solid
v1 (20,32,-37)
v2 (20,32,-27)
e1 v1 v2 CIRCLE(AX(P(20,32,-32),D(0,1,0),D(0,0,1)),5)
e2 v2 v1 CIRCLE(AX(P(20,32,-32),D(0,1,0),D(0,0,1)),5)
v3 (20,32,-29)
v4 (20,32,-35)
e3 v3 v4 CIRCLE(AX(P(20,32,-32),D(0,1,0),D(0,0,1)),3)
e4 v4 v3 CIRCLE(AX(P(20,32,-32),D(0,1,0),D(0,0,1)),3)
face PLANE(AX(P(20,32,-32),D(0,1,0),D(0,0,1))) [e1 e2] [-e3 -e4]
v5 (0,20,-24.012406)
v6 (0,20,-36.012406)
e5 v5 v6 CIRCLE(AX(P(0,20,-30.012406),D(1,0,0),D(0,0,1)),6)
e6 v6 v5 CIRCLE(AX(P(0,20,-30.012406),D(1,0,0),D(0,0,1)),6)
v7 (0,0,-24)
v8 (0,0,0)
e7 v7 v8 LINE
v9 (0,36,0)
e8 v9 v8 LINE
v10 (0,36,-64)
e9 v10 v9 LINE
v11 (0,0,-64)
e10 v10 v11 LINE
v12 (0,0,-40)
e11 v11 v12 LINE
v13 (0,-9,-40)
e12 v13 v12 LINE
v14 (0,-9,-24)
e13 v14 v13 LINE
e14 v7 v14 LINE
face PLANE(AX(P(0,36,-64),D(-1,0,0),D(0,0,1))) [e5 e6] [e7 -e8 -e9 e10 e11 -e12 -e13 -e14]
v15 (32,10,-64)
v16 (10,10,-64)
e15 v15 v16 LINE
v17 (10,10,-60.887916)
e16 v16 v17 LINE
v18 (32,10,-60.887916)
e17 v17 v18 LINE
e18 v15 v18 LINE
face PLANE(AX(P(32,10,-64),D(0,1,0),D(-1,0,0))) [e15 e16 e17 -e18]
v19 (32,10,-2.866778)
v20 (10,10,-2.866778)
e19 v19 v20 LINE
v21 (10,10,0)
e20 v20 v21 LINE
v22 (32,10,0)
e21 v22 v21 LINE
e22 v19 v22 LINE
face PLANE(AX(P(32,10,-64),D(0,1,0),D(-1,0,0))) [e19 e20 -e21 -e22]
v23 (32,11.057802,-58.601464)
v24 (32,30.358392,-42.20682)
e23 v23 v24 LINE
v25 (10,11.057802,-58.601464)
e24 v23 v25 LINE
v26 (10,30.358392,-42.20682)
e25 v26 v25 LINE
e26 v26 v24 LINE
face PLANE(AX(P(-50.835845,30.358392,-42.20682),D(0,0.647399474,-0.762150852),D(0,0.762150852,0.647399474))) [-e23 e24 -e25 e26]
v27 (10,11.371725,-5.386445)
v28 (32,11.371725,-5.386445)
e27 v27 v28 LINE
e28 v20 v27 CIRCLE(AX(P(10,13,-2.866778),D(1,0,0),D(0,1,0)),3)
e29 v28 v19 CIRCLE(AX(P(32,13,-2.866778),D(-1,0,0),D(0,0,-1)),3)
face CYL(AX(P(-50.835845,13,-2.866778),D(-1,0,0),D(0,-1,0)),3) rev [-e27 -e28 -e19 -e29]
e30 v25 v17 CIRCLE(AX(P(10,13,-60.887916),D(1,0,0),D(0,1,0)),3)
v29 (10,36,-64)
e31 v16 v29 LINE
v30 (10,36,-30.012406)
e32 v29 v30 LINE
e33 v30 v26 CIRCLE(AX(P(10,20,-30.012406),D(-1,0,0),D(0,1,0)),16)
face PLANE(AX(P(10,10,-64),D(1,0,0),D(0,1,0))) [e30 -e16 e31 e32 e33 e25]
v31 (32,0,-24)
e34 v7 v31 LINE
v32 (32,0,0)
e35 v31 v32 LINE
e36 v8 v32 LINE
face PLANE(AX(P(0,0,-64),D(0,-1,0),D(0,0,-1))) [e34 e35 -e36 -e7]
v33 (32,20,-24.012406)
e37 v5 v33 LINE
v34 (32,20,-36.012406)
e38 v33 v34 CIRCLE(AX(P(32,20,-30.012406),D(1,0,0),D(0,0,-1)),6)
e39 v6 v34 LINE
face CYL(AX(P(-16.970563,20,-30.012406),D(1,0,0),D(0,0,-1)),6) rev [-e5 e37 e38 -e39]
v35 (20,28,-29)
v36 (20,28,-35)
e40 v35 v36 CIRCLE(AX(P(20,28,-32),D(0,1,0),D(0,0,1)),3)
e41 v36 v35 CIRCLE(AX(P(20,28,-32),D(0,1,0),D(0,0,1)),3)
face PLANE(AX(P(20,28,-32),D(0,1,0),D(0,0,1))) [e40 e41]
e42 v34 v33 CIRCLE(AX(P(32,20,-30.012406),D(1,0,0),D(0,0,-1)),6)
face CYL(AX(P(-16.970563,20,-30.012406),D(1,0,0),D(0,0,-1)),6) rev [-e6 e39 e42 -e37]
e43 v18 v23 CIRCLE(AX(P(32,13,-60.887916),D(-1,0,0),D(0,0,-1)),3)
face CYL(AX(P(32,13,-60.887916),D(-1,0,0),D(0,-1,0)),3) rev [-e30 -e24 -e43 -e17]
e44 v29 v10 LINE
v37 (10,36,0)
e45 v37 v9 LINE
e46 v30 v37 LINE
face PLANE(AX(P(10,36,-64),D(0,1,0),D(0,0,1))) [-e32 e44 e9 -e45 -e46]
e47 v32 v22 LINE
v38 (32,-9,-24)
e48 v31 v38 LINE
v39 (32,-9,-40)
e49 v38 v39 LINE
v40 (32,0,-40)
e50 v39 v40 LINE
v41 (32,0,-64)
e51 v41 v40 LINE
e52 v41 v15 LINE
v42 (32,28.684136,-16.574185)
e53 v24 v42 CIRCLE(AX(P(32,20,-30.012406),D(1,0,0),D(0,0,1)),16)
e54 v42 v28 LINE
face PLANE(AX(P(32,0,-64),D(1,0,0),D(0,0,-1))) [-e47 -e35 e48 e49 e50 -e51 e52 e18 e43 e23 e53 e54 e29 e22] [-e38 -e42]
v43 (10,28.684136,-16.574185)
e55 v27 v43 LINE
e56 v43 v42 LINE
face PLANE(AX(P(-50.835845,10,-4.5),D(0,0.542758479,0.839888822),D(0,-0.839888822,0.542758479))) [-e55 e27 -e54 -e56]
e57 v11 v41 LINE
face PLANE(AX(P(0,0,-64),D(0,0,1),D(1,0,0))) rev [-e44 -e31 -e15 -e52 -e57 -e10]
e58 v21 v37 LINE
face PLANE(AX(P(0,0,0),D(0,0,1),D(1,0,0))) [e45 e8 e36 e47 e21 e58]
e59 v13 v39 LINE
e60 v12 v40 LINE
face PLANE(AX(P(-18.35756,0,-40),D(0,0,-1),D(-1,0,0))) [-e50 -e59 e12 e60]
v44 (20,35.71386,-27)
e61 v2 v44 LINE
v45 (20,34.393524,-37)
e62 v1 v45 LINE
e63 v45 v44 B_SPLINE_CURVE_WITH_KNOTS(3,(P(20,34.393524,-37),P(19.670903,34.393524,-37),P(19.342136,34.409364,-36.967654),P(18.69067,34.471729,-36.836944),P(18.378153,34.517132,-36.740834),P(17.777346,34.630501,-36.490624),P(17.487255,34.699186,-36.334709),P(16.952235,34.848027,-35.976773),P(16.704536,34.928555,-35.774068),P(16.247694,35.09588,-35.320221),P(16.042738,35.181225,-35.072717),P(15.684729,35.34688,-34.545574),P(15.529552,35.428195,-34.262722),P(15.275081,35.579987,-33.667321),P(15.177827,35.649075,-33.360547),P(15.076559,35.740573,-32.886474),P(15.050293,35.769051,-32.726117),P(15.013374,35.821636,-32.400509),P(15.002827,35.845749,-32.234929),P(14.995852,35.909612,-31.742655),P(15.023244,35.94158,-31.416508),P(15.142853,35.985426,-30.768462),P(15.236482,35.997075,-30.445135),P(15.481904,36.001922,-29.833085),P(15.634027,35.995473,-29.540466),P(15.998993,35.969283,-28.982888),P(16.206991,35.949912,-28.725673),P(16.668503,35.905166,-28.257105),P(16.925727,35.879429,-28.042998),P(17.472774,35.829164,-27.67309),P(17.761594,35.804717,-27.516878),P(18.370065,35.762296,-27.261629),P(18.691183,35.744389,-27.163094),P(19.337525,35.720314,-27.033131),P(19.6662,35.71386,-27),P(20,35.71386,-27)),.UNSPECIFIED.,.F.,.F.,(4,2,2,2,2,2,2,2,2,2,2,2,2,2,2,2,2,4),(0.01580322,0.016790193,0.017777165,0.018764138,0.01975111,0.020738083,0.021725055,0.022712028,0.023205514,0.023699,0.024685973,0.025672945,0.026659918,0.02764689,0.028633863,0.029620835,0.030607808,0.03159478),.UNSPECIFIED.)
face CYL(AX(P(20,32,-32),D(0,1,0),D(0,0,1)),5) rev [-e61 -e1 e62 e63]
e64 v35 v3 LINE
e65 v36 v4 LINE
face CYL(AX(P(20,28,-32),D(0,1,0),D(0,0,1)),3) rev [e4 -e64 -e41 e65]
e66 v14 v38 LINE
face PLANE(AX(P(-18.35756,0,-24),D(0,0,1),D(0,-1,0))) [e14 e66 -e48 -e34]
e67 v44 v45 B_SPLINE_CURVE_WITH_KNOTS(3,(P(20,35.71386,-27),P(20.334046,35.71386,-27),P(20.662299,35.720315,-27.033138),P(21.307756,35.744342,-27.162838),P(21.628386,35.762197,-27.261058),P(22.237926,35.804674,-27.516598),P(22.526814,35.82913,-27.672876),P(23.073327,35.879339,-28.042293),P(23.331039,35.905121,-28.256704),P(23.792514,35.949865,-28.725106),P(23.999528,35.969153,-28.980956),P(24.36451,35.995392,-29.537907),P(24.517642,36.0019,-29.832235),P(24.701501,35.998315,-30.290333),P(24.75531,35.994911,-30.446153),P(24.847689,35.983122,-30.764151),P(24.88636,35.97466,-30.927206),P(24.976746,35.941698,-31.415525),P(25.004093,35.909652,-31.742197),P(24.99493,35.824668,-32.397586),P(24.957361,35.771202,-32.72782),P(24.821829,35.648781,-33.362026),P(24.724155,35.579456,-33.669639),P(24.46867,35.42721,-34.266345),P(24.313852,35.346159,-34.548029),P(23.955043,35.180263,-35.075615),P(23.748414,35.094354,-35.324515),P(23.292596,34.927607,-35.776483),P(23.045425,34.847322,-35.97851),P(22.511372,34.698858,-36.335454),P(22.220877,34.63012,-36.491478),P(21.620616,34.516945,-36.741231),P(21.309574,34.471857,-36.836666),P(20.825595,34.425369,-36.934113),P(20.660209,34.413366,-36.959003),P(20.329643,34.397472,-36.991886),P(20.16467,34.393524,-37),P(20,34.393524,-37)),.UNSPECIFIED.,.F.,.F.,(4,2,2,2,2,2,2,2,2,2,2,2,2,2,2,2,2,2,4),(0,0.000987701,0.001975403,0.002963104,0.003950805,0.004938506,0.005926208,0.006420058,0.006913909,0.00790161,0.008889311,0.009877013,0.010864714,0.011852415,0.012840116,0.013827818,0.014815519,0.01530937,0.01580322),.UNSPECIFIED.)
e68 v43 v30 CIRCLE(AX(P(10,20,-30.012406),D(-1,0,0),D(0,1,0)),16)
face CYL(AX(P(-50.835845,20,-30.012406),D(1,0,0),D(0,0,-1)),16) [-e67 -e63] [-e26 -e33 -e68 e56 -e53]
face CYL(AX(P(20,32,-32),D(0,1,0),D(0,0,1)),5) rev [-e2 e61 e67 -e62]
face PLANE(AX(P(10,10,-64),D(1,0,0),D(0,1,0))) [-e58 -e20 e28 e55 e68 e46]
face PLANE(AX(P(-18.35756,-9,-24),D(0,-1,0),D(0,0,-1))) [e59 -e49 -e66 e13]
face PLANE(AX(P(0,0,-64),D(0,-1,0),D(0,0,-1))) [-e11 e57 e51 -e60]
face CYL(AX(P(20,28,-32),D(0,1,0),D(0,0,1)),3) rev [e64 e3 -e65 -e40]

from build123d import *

# Parameters (mm, degrees)
JAW_BODY_DEPTH         = 64
PIVOT_BOSS_DEPTH       = 22
PIVOT_BORE_SKETCH_R    = 6
PIVOT_BORE_12_DEPTH    = 32
GUIDE_KEY_SKETCH_W     = 16
GUIDE_KEY_SKETCH_H     = 9
GUIDE_KEY_DEPTH        = 32
PIVOT_BOSS_FILLET_R3_R = 3
COUNTERBORE_SKETCH_R   = 5
COUNTERBORE_10X4_DEPTH = 4
SCREW_HOLE_SKETCH_R    = 3
SCREW_HOLE_6X4_DEPTH   = 4


with BuildPart() as part:
    # Jaw Body Profile Sketch → Jaw Body (new body)
    with BuildSketch(Plane.XY):
        Polygon((0, 0), (32, 0), (32, 10), (10, 10), (10, 36), (0, 36), align=None)
    extrude(amount=-JAW_BODY_DEPTH)

    # Pivot Boss Sketch → Pivot Boss (add)
    with BuildSketch(Plane(origin=(32, 0, 0), x_dir=(0, 0, -1), z_dir=(1, 0, 0))):
        with BuildLine():
            Line((4.5, 10), (16.574185034, 28.68413566))
            ThreePointArc((16.574185034, 28.68413566), (28.969550727, 35.965977968), (42.206819819, 30.358391585))
            Line((42.206819819, 30.358391585), (59.5, 10))
            Line((59.5, 10), (4.5, 10))
        make_face()
    extrude(amount=-PIVOT_BOSS_DEPTH)

    # Pivot Bore Sketch → Pivot Bore Ø12 (cut)
    with BuildSketch(Plane(origin=(32, 0, 0), x_dir=(0, 0, -1), z_dir=(1, 0, 0))):
        with Locations((30.01240619, 20)):
            Circle(PIVOT_BORE_SKETCH_R)
    extrude(amount=-PIVOT_BORE_12_DEPTH, mode=Mode.SUBTRACT)

    # Guide Key Sketch → Guide Key (add)
    with BuildSketch(Plane(origin=(32, 0, 0), x_dir=(0, 0, -1), z_dir=(1, 0, 0))):
        with Locations((32, -4.5)):
            Rectangle(GUIDE_KEY_SKETCH_W, GUIDE_KEY_SKETCH_H)
    extrude(amount=-GUIDE_KEY_DEPTH)

    # Pivot Boss Fillet R3
    pivot_boss_fillet_r3_edges = [part.edges().sort_by_distance(p)[0] for p in [
        (21, 10, -59.5),
        (21, 10, -4.5),
    ]]
    fillet(pivot_boss_fillet_r3_edges, radius=PIVOT_BOSS_FILLET_R3_R)

    # Counterbore Sketch → Counterbore Ø10x4 (cut)
    with BuildSketch(Plane(origin=(0, 36, 0), x_dir=(1, 0, 0), z_dir=(0, 1, 0))):
        with Locations(Location((20, 32, 0), (0, 0, 270))):
            Circle(COUNTERBORE_SKETCH_R)
    extrude(amount=-COUNTERBORE_10X4_DEPTH, mode=Mode.SUBTRACT)

    # Screw Hole Sketch → Screw Hole Ø6x4 (cut)
    with BuildSketch(Plane(origin=(0, 32, 0), x_dir=(1, 0, 0), z_dir=(0, 1, 0))):
        with Locations(Location((20, 32, 0), (0, 0, 270))):
            Circle(SCREW_HOLE_SKETCH_R)
    extrude(amount=-SCREW_HOLE_6X4_DEPTH, mode=Mode.SUBTRACT)


solid = part.part
